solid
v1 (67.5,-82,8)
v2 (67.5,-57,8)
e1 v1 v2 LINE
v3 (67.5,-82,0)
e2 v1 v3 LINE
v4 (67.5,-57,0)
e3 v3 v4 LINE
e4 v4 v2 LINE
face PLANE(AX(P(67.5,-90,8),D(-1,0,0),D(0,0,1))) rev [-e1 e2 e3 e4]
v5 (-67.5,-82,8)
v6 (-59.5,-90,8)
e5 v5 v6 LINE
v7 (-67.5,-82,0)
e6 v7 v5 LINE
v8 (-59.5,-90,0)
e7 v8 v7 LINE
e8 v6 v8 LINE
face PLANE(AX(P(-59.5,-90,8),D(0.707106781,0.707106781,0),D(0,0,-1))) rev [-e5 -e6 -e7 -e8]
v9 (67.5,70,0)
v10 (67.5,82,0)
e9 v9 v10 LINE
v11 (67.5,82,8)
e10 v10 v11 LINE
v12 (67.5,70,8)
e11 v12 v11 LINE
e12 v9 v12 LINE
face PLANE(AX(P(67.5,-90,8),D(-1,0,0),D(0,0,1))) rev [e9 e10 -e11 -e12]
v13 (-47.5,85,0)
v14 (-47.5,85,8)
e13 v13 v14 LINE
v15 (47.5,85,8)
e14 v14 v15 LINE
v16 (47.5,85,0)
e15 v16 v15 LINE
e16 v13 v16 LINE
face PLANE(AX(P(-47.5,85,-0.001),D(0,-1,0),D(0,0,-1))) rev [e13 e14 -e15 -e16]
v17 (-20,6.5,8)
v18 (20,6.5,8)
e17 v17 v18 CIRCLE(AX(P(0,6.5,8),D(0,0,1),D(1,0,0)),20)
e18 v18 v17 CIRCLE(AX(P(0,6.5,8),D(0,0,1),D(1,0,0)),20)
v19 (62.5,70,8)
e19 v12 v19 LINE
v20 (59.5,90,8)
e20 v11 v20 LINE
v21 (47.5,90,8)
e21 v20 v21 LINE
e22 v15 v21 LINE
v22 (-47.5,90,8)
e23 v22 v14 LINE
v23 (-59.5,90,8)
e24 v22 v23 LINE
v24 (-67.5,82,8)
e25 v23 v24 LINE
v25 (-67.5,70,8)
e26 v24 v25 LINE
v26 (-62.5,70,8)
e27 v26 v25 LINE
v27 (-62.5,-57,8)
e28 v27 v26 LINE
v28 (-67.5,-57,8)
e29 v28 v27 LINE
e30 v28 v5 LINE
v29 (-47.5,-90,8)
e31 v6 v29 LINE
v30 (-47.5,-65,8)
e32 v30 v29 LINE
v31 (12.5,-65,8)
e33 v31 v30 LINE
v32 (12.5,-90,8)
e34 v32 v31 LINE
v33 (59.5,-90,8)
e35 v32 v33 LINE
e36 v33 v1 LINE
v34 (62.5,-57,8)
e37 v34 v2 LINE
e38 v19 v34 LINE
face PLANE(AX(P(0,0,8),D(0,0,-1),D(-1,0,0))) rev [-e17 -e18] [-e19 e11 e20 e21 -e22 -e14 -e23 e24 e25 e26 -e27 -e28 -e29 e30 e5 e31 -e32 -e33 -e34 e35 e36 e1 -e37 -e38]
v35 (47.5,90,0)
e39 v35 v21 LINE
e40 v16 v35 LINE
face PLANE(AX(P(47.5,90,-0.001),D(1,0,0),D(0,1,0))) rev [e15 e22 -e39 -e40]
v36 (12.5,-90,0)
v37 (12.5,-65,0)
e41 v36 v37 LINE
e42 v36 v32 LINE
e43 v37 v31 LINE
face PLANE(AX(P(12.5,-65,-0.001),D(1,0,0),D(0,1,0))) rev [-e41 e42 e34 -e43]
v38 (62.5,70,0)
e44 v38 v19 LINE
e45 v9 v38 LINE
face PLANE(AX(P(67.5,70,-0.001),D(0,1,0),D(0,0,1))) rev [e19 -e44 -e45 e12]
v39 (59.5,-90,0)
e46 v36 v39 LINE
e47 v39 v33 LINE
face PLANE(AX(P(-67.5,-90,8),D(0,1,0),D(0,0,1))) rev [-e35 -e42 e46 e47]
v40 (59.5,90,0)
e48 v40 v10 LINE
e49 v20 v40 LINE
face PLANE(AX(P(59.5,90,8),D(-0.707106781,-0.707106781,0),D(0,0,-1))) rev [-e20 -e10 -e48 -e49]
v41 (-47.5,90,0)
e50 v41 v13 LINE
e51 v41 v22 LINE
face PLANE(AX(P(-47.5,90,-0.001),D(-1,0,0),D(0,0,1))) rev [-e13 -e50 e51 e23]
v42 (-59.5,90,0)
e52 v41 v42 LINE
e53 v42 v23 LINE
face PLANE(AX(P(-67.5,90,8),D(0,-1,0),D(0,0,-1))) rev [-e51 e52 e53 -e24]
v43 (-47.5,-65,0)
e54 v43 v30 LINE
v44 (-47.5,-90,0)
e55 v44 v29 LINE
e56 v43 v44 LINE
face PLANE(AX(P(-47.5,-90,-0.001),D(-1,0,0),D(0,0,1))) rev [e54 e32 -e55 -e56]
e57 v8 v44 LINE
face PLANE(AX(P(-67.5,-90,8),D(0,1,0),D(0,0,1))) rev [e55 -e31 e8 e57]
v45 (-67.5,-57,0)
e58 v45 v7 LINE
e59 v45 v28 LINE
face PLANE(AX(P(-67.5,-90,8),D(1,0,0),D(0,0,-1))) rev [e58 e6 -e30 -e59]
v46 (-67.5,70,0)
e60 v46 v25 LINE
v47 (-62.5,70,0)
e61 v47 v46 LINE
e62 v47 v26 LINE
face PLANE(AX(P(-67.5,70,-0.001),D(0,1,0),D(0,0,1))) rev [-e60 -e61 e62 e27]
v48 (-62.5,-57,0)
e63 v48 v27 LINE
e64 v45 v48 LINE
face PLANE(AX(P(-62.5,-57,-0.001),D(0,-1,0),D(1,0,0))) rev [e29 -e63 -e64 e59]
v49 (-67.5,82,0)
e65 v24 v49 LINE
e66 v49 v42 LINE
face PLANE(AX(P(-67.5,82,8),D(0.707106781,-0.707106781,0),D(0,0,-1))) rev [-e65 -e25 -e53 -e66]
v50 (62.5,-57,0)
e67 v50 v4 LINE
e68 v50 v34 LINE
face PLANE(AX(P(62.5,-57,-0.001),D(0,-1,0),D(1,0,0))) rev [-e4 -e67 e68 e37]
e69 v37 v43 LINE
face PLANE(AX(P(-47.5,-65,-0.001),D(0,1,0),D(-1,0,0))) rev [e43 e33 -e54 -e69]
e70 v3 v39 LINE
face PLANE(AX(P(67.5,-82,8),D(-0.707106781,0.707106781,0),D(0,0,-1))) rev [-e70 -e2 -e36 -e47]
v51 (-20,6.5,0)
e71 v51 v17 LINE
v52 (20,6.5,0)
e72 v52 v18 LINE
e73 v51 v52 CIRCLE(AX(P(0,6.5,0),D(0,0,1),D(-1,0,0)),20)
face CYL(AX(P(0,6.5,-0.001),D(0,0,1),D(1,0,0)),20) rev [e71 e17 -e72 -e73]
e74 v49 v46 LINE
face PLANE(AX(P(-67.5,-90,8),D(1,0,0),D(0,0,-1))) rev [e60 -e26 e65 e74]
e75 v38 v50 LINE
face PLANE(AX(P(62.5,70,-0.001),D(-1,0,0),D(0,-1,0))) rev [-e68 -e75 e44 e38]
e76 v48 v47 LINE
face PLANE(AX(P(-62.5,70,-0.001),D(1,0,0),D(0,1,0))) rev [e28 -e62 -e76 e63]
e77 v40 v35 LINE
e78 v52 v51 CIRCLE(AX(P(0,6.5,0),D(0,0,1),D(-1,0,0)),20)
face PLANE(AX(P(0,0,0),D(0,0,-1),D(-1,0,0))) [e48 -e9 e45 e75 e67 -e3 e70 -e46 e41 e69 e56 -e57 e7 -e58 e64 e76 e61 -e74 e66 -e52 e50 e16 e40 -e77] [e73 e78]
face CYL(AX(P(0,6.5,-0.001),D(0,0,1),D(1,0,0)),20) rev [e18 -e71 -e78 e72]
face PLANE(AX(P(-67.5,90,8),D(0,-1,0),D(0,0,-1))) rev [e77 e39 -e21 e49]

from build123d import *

# Parameters (mm, degrees)
SKETCH_1_W          = 135
SKETCH_1_H          = 180
EXTRUDE_1_DEPTH     = 8
CUT_EXTRUDE_1_REACH = 114.784
SKETCH_2_W          = 95
SKETCH_2_H          = 5
SKETCH_2_W_2        = 60
SKETCH_2_H_2        = 25
SKETCH_2_W_3        = 5
SKETCH_2_H_3        = 127
CHAMFER_1_SIZE      = 8
CUT_EXTRUDE_2_REACH = 114.784
SKETCH_3_R          = 20


with BuildPart() as part:
    # 草图1 → 凸台-拉伸1 (new body)
    with BuildSketch(Plane.XY):
        Rectangle(SKETCH_1_W, SKETCH_1_H)
    extrude(amount=EXTRUDE_1_DEPTH)

    # 草图2 → 切除-拉伸1 (cut, up to next)
    with BuildSketch(Plane.XY.offset(8), mode=Mode.PRIVATE) as cut_extrude_1_sk1:
        with Locations((0, 87.5)):
            Rectangle(SKETCH_2_W, SKETCH_2_H)
    cut_extrude_1_tool1 = extrude(cut_extrude_1_sk1.sketch, amount=-CUT_EXTRUDE_1_REACH, mode=Mode.PRIVATE) & part.part
    # 草图2 → 切除-拉伸1 (cut, up to next)
    with BuildSketch(Plane.XY.offset(8), mode=Mode.PRIVATE) as cut_extrude_1_sk2:
        with Locations((-17.5, -77.5)):
            Rectangle(SKETCH_2_W_2, SKETCH_2_H_2)
    cut_extrude_1_tool2 = extrude(cut_extrude_1_sk2.sketch, amount=-CUT_EXTRUDE_1_REACH, mode=Mode.PRIVATE) & part.part
    # 草图2 → 切除-拉伸1 (cut, up to next)
    with BuildSketch(Plane.XY.offset(8), mode=Mode.PRIVATE) as cut_extrude_1_sk3:
        with Locations((-65, 6.5)):
            Rectangle(SKETCH_2_W_3, SKETCH_2_H_3)
    cut_extrude_1_tool3 = extrude(cut_extrude_1_sk3.sketch, amount=-CUT_EXTRUDE_1_REACH, mode=Mode.PRIVATE) & part.part
    # 草图2 → 切除-拉伸1 (cut, up to next)
    with BuildSketch(Plane.XY.offset(8), mode=Mode.PRIVATE) as cut_extrude_1_sk4:
        with Locations((65, 6.5)):
            Rectangle(SKETCH_2_W_3, SKETCH_2_H_3)
    cut_extrude_1_tool4 = extrude(cut_extrude_1_sk4.sketch, amount=-CUT_EXTRUDE_1_REACH, mode=Mode.PRIVATE) & part.part
    add(cut_extrude_1_tool1.solids().sort_by_distance((0, 87.5, 8))[0], mode=Mode.SUBTRACT)
    add(cut_extrude_1_tool2.solids().sort_by_distance((-17.5, -77.5, 8))[0], mode=Mode.SUBTRACT)
    add(cut_extrude_1_tool3.solids().sort_by_distance((-65, 6.5, 8))[0], mode=Mode.SUBTRACT)
    add(cut_extrude_1_tool4.solids().sort_by_distance((65, 6.5, 8))[0], mode=Mode.SUBTRACT)

    # 倒角1
    chamfer_1_edges = [part.edges().sort_by_distance(p)[0] for p in [
        (67.5, -90, 4),
        (-67.5, -90, 4),
        (-67.5, 90, 4),
        (67.5, 90, 4),
    ]]
    chamfer(chamfer_1_edges, length=CHAMFER_1_SIZE)

    # 草图3 → 切除-拉伸2 (cut, up to next)
    with BuildSketch(Plane.XY.offset(8), mode=Mode.PRIVATE) as cut_extrude_2_sk1:
        with Locations((0, 6.5)):
            Circle(SKETCH_3_R)
    cut_extrude_2_tool1 = extrude(cut_extrude_2_sk1.sketch, amount=-CUT_EXTRUDE_2_REACH, mode=Mode.PRIVATE) & part.part
    add(cut_extrude_2_tool1.solids().sort_by_distance((0, 6.5, 8))[0], mode=Mode.SUBTRACT)


solid = part.part
